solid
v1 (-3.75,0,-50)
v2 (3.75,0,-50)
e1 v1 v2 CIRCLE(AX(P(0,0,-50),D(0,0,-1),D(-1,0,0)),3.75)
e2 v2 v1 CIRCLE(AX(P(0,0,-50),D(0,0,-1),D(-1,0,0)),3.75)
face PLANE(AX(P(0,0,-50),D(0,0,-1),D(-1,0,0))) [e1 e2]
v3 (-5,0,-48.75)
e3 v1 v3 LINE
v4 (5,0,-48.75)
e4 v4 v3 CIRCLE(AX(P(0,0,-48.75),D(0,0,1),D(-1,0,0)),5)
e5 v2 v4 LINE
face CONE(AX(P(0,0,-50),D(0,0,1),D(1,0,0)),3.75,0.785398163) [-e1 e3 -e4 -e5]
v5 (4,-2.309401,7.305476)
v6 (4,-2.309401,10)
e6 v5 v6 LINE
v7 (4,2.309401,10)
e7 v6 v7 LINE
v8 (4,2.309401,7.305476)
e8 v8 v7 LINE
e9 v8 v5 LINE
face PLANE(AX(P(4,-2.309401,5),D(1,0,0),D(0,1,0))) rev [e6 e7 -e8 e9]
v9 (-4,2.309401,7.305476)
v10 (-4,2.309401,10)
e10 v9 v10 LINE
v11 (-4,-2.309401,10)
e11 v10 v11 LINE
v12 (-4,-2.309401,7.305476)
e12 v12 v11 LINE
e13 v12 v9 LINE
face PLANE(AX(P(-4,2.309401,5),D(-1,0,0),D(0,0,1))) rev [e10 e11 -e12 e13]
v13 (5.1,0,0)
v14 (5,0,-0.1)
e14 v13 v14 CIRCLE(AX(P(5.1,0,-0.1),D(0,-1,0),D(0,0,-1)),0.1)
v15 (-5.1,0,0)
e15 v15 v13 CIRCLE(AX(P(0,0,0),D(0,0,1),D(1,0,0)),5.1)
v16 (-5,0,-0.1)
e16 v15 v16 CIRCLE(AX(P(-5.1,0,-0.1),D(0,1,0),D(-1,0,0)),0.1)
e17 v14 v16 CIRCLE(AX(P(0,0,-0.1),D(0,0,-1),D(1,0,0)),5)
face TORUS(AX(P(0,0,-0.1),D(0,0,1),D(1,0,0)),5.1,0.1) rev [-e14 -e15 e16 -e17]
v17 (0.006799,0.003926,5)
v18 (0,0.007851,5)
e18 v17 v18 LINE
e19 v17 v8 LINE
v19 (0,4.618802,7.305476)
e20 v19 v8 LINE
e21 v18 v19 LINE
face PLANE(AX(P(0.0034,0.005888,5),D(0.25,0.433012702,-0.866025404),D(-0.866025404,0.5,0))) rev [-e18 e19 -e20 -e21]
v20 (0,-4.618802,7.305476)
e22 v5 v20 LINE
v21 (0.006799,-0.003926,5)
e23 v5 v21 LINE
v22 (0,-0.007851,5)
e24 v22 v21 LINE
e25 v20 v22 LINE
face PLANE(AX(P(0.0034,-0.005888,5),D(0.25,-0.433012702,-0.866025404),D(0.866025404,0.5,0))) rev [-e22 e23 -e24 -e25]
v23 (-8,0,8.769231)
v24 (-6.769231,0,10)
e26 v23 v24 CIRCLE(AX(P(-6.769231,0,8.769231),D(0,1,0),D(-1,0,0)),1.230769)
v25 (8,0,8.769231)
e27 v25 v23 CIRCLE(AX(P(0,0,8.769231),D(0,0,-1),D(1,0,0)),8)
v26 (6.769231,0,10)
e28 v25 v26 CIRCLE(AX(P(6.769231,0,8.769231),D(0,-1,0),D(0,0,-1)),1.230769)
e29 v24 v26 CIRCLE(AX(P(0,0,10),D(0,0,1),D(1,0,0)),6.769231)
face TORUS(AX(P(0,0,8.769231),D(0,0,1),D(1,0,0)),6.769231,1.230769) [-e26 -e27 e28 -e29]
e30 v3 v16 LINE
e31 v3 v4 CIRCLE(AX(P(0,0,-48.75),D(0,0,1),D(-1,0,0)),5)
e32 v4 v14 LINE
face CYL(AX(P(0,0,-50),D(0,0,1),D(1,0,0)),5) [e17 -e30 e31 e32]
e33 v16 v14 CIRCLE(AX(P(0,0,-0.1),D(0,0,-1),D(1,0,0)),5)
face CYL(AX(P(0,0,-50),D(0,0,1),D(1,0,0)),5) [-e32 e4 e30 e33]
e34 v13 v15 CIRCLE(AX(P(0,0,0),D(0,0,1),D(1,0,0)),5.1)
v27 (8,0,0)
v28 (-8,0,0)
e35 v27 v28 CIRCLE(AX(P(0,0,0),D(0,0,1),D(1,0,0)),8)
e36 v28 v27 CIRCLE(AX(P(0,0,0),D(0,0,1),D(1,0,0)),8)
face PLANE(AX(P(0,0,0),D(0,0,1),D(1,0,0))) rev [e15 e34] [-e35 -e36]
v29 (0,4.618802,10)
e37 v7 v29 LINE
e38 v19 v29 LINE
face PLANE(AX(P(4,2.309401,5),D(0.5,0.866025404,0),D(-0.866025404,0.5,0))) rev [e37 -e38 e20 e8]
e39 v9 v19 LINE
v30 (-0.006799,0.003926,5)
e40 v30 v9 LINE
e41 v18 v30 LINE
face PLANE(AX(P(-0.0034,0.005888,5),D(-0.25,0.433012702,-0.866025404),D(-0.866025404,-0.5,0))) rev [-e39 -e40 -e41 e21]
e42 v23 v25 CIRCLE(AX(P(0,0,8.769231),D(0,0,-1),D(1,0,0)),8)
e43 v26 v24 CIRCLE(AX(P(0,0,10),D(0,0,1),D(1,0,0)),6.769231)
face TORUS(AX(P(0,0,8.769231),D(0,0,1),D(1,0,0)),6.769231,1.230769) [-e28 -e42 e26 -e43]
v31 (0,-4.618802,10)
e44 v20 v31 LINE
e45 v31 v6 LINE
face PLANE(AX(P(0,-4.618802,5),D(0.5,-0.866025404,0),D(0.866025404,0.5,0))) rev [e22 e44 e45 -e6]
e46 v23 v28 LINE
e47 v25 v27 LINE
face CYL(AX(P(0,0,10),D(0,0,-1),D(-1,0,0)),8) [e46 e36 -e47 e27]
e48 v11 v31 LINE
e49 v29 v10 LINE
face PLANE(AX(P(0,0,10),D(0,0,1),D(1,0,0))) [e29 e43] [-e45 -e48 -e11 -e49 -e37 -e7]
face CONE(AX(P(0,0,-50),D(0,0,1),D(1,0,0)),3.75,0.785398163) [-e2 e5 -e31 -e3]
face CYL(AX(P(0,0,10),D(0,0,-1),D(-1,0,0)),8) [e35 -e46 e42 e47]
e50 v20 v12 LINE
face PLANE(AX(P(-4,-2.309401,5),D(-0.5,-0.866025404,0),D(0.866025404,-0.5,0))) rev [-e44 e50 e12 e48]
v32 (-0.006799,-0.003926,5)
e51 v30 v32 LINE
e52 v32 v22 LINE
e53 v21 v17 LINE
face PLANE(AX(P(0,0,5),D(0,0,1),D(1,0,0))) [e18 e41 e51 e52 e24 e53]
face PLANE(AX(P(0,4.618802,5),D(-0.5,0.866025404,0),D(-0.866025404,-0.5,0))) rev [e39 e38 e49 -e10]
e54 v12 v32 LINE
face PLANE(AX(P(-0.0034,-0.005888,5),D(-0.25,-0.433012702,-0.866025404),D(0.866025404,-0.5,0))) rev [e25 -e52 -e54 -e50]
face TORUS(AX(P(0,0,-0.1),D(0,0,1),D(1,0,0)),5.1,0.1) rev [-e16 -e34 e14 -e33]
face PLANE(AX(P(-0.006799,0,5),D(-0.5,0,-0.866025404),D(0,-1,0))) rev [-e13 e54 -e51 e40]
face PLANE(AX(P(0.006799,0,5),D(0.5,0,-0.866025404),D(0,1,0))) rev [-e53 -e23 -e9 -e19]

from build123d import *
from OCP.BRepFilletAPI import BRepFilletAPI_MakeChamfer

# Parameters (mm, degrees)
SKETCH1_R           = 8
BOSS_EXTRUDE1_DEPTH = 10
CUT_EXTRUDE1_DEPTH  = 5
SKETCH3_R           = 5
BOSS_EXTRUDE2_DEPTH = 50
CHAMFER1_SIZE       = 1.25
FILLET1_R           = 1.230769231
CHAMFER2_SIZE       = 2.305475504
CHAMFER2_SIZE2      = 3.993200709
FILLET2_R           = 0.1


with BuildPart() as part:
    # Sketch1 → Boss-Extrude1 (new body)
    with BuildSketch(Plane.XY):
        Circle(SKETCH1_R)
    extrude(amount=BOSS_EXTRUDE1_DEPTH)

    # Sketch2 → Cut-Extrude1 (cut)
    with BuildSketch(Plane.XY.offset(10)):
        Polygon((4, 2.309401077), (0, 4.618802154), (-4, 2.309401077), (-4, -2.309401077), (0, -4.618802154), (4, -2.309401077), align=None)
    extrude(amount=-CUT_EXTRUDE1_DEPTH, mode=Mode.SUBTRACT)

    # Sketch3 → Boss-Extrude2 (add)
    with BuildSketch(Plane(origin=(0, 0, 0), x_dir=(-1, 0, 0), z_dir=(0, 0, -1))):
        with Locations(Location((0, 0, 0), (0, 0, 180))):
            Circle(SKETCH3_R)
    extrude(amount=BOSS_EXTRUDE2_DEPTH)

    # Chamfer1
    chamfer1_edges = [part.edges().sort_by_distance(p)[0] for p in [
        (-5, 0, -50),
    ]]
    chamfer(chamfer1_edges, length=CHAMFER1_SIZE)

    # Fillet1
    fillet1_edges = [part.edges().sort_by_distance(p)[0] for p in [
        (-8, 0, 10),
    ]]
    fillet(fillet1_edges, radius=FILLET1_R)

    # Chamfer2: one chamfer whose edges measure the first distance from different faces: ONE call of the kernel's chamfer builder (chamfer() names one face for all edges)
    chamfer2_edges_1 = [part.edges().sort_by_distance(p)[0] for p in [
        (-2, 3.464101615, 5),
    ]]
    chamfer2_side_1 = [part.faces().sort_by_distance(p)[0] for p in [
        (-2, 3.464101615, 7.5),
    ]]
    chamfer2_edges_2 = [part.edges().sort_by_distance(p)[0] for p in [
        (2, 3.464101615, 5),
    ]]
    chamfer2_side_2 = [part.faces().sort_by_distance(p)[0] for p in [
        (2, 3.464101615, 7.5),
    ]]
    chamfer2_edges_3 = [part.edges().sort_by_distance(p)[0] for p in [
        (4, 0, 5),
    ]]
    chamfer2_side_3 = [part.faces().sort_by_distance(p)[0] for p in [
        (4, 0, 7.5),
    ]]
    chamfer2_edges_4 = [part.edges().sort_by_distance(p)[0] for p in [
        (2, -3.464101615, 5),
    ]]
    chamfer2_side_4 = [part.faces().sort_by_distance(p)[0] for p in [
        (2, -3.464101615, 7.5),
    ]]
    chamfer2_edges_5 = [part.edges().sort_by_distance(p)[0] for p in [
        (-2, -3.464101615, 5),
    ]]
    chamfer2_side_5 = [part.faces().sort_by_distance(p)[0] for p in [
        (-2, -3.464101615, 7.5),
    ]]
    chamfer2_edges_6 = [part.edges().sort_by_distance(p)[0] for p in [
        (-4, 0, 5),
    ]]
    chamfer2_side_6 = [part.faces().sort_by_distance(p)[0] for p in [
        (-4, 0, 7.5),
    ]]
    chamfer2 = BRepFilletAPI_MakeChamfer(part.part.solid().wrapped)
    for e in chamfer2_edges_1:
        chamfer2.Add(CHAMFER2_SIZE, CHAMFER2_SIZE2, e.wrapped, chamfer2_side_1[0].wrapped)  # the first distance lies on this face
    for e in chamfer2_edges_2:
        chamfer2.Add(CHAMFER2_SIZE, CHAMFER2_SIZE2, e.wrapped, chamfer2_side_2[0].wrapped)  # the first distance lies on this face
    for e in chamfer2_edges_3:
        chamfer2.Add(CHAMFER2_SIZE, CHAMFER2_SIZE2, e.wrapped, chamfer2_side_3[0].wrapped)  # the first distance lies on this face
    for e in chamfer2_edges_4:
        chamfer2.Add(CHAMFER2_SIZE, CHAMFER2_SIZE2, e.wrapped, chamfer2_side_4[0].wrapped)  # the first distance lies on this face
    for e in chamfer2_edges_5:
        chamfer2.Add(CHAMFER2_SIZE, CHAMFER2_SIZE2, e.wrapped, chamfer2_side_5[0].wrapped)  # the first distance lies on this face
    for e in chamfer2_edges_6:
        chamfer2.Add(CHAMFER2_SIZE, CHAMFER2_SIZE2, e.wrapped, chamfer2_side_6[0].wrapped)  # the first distance lies on this face
    add(Compound.cast(chamfer2.Shape()), mode=Mode.REPLACE)

    # Fillet2
    fillet2_edges = [part.edges().sort_by_distance(p)[0] for p in [
        (-5, 0, 0),
    ]]
    fillet(fillet2_edges, radius=FILLET2_R)


solid = part.part
